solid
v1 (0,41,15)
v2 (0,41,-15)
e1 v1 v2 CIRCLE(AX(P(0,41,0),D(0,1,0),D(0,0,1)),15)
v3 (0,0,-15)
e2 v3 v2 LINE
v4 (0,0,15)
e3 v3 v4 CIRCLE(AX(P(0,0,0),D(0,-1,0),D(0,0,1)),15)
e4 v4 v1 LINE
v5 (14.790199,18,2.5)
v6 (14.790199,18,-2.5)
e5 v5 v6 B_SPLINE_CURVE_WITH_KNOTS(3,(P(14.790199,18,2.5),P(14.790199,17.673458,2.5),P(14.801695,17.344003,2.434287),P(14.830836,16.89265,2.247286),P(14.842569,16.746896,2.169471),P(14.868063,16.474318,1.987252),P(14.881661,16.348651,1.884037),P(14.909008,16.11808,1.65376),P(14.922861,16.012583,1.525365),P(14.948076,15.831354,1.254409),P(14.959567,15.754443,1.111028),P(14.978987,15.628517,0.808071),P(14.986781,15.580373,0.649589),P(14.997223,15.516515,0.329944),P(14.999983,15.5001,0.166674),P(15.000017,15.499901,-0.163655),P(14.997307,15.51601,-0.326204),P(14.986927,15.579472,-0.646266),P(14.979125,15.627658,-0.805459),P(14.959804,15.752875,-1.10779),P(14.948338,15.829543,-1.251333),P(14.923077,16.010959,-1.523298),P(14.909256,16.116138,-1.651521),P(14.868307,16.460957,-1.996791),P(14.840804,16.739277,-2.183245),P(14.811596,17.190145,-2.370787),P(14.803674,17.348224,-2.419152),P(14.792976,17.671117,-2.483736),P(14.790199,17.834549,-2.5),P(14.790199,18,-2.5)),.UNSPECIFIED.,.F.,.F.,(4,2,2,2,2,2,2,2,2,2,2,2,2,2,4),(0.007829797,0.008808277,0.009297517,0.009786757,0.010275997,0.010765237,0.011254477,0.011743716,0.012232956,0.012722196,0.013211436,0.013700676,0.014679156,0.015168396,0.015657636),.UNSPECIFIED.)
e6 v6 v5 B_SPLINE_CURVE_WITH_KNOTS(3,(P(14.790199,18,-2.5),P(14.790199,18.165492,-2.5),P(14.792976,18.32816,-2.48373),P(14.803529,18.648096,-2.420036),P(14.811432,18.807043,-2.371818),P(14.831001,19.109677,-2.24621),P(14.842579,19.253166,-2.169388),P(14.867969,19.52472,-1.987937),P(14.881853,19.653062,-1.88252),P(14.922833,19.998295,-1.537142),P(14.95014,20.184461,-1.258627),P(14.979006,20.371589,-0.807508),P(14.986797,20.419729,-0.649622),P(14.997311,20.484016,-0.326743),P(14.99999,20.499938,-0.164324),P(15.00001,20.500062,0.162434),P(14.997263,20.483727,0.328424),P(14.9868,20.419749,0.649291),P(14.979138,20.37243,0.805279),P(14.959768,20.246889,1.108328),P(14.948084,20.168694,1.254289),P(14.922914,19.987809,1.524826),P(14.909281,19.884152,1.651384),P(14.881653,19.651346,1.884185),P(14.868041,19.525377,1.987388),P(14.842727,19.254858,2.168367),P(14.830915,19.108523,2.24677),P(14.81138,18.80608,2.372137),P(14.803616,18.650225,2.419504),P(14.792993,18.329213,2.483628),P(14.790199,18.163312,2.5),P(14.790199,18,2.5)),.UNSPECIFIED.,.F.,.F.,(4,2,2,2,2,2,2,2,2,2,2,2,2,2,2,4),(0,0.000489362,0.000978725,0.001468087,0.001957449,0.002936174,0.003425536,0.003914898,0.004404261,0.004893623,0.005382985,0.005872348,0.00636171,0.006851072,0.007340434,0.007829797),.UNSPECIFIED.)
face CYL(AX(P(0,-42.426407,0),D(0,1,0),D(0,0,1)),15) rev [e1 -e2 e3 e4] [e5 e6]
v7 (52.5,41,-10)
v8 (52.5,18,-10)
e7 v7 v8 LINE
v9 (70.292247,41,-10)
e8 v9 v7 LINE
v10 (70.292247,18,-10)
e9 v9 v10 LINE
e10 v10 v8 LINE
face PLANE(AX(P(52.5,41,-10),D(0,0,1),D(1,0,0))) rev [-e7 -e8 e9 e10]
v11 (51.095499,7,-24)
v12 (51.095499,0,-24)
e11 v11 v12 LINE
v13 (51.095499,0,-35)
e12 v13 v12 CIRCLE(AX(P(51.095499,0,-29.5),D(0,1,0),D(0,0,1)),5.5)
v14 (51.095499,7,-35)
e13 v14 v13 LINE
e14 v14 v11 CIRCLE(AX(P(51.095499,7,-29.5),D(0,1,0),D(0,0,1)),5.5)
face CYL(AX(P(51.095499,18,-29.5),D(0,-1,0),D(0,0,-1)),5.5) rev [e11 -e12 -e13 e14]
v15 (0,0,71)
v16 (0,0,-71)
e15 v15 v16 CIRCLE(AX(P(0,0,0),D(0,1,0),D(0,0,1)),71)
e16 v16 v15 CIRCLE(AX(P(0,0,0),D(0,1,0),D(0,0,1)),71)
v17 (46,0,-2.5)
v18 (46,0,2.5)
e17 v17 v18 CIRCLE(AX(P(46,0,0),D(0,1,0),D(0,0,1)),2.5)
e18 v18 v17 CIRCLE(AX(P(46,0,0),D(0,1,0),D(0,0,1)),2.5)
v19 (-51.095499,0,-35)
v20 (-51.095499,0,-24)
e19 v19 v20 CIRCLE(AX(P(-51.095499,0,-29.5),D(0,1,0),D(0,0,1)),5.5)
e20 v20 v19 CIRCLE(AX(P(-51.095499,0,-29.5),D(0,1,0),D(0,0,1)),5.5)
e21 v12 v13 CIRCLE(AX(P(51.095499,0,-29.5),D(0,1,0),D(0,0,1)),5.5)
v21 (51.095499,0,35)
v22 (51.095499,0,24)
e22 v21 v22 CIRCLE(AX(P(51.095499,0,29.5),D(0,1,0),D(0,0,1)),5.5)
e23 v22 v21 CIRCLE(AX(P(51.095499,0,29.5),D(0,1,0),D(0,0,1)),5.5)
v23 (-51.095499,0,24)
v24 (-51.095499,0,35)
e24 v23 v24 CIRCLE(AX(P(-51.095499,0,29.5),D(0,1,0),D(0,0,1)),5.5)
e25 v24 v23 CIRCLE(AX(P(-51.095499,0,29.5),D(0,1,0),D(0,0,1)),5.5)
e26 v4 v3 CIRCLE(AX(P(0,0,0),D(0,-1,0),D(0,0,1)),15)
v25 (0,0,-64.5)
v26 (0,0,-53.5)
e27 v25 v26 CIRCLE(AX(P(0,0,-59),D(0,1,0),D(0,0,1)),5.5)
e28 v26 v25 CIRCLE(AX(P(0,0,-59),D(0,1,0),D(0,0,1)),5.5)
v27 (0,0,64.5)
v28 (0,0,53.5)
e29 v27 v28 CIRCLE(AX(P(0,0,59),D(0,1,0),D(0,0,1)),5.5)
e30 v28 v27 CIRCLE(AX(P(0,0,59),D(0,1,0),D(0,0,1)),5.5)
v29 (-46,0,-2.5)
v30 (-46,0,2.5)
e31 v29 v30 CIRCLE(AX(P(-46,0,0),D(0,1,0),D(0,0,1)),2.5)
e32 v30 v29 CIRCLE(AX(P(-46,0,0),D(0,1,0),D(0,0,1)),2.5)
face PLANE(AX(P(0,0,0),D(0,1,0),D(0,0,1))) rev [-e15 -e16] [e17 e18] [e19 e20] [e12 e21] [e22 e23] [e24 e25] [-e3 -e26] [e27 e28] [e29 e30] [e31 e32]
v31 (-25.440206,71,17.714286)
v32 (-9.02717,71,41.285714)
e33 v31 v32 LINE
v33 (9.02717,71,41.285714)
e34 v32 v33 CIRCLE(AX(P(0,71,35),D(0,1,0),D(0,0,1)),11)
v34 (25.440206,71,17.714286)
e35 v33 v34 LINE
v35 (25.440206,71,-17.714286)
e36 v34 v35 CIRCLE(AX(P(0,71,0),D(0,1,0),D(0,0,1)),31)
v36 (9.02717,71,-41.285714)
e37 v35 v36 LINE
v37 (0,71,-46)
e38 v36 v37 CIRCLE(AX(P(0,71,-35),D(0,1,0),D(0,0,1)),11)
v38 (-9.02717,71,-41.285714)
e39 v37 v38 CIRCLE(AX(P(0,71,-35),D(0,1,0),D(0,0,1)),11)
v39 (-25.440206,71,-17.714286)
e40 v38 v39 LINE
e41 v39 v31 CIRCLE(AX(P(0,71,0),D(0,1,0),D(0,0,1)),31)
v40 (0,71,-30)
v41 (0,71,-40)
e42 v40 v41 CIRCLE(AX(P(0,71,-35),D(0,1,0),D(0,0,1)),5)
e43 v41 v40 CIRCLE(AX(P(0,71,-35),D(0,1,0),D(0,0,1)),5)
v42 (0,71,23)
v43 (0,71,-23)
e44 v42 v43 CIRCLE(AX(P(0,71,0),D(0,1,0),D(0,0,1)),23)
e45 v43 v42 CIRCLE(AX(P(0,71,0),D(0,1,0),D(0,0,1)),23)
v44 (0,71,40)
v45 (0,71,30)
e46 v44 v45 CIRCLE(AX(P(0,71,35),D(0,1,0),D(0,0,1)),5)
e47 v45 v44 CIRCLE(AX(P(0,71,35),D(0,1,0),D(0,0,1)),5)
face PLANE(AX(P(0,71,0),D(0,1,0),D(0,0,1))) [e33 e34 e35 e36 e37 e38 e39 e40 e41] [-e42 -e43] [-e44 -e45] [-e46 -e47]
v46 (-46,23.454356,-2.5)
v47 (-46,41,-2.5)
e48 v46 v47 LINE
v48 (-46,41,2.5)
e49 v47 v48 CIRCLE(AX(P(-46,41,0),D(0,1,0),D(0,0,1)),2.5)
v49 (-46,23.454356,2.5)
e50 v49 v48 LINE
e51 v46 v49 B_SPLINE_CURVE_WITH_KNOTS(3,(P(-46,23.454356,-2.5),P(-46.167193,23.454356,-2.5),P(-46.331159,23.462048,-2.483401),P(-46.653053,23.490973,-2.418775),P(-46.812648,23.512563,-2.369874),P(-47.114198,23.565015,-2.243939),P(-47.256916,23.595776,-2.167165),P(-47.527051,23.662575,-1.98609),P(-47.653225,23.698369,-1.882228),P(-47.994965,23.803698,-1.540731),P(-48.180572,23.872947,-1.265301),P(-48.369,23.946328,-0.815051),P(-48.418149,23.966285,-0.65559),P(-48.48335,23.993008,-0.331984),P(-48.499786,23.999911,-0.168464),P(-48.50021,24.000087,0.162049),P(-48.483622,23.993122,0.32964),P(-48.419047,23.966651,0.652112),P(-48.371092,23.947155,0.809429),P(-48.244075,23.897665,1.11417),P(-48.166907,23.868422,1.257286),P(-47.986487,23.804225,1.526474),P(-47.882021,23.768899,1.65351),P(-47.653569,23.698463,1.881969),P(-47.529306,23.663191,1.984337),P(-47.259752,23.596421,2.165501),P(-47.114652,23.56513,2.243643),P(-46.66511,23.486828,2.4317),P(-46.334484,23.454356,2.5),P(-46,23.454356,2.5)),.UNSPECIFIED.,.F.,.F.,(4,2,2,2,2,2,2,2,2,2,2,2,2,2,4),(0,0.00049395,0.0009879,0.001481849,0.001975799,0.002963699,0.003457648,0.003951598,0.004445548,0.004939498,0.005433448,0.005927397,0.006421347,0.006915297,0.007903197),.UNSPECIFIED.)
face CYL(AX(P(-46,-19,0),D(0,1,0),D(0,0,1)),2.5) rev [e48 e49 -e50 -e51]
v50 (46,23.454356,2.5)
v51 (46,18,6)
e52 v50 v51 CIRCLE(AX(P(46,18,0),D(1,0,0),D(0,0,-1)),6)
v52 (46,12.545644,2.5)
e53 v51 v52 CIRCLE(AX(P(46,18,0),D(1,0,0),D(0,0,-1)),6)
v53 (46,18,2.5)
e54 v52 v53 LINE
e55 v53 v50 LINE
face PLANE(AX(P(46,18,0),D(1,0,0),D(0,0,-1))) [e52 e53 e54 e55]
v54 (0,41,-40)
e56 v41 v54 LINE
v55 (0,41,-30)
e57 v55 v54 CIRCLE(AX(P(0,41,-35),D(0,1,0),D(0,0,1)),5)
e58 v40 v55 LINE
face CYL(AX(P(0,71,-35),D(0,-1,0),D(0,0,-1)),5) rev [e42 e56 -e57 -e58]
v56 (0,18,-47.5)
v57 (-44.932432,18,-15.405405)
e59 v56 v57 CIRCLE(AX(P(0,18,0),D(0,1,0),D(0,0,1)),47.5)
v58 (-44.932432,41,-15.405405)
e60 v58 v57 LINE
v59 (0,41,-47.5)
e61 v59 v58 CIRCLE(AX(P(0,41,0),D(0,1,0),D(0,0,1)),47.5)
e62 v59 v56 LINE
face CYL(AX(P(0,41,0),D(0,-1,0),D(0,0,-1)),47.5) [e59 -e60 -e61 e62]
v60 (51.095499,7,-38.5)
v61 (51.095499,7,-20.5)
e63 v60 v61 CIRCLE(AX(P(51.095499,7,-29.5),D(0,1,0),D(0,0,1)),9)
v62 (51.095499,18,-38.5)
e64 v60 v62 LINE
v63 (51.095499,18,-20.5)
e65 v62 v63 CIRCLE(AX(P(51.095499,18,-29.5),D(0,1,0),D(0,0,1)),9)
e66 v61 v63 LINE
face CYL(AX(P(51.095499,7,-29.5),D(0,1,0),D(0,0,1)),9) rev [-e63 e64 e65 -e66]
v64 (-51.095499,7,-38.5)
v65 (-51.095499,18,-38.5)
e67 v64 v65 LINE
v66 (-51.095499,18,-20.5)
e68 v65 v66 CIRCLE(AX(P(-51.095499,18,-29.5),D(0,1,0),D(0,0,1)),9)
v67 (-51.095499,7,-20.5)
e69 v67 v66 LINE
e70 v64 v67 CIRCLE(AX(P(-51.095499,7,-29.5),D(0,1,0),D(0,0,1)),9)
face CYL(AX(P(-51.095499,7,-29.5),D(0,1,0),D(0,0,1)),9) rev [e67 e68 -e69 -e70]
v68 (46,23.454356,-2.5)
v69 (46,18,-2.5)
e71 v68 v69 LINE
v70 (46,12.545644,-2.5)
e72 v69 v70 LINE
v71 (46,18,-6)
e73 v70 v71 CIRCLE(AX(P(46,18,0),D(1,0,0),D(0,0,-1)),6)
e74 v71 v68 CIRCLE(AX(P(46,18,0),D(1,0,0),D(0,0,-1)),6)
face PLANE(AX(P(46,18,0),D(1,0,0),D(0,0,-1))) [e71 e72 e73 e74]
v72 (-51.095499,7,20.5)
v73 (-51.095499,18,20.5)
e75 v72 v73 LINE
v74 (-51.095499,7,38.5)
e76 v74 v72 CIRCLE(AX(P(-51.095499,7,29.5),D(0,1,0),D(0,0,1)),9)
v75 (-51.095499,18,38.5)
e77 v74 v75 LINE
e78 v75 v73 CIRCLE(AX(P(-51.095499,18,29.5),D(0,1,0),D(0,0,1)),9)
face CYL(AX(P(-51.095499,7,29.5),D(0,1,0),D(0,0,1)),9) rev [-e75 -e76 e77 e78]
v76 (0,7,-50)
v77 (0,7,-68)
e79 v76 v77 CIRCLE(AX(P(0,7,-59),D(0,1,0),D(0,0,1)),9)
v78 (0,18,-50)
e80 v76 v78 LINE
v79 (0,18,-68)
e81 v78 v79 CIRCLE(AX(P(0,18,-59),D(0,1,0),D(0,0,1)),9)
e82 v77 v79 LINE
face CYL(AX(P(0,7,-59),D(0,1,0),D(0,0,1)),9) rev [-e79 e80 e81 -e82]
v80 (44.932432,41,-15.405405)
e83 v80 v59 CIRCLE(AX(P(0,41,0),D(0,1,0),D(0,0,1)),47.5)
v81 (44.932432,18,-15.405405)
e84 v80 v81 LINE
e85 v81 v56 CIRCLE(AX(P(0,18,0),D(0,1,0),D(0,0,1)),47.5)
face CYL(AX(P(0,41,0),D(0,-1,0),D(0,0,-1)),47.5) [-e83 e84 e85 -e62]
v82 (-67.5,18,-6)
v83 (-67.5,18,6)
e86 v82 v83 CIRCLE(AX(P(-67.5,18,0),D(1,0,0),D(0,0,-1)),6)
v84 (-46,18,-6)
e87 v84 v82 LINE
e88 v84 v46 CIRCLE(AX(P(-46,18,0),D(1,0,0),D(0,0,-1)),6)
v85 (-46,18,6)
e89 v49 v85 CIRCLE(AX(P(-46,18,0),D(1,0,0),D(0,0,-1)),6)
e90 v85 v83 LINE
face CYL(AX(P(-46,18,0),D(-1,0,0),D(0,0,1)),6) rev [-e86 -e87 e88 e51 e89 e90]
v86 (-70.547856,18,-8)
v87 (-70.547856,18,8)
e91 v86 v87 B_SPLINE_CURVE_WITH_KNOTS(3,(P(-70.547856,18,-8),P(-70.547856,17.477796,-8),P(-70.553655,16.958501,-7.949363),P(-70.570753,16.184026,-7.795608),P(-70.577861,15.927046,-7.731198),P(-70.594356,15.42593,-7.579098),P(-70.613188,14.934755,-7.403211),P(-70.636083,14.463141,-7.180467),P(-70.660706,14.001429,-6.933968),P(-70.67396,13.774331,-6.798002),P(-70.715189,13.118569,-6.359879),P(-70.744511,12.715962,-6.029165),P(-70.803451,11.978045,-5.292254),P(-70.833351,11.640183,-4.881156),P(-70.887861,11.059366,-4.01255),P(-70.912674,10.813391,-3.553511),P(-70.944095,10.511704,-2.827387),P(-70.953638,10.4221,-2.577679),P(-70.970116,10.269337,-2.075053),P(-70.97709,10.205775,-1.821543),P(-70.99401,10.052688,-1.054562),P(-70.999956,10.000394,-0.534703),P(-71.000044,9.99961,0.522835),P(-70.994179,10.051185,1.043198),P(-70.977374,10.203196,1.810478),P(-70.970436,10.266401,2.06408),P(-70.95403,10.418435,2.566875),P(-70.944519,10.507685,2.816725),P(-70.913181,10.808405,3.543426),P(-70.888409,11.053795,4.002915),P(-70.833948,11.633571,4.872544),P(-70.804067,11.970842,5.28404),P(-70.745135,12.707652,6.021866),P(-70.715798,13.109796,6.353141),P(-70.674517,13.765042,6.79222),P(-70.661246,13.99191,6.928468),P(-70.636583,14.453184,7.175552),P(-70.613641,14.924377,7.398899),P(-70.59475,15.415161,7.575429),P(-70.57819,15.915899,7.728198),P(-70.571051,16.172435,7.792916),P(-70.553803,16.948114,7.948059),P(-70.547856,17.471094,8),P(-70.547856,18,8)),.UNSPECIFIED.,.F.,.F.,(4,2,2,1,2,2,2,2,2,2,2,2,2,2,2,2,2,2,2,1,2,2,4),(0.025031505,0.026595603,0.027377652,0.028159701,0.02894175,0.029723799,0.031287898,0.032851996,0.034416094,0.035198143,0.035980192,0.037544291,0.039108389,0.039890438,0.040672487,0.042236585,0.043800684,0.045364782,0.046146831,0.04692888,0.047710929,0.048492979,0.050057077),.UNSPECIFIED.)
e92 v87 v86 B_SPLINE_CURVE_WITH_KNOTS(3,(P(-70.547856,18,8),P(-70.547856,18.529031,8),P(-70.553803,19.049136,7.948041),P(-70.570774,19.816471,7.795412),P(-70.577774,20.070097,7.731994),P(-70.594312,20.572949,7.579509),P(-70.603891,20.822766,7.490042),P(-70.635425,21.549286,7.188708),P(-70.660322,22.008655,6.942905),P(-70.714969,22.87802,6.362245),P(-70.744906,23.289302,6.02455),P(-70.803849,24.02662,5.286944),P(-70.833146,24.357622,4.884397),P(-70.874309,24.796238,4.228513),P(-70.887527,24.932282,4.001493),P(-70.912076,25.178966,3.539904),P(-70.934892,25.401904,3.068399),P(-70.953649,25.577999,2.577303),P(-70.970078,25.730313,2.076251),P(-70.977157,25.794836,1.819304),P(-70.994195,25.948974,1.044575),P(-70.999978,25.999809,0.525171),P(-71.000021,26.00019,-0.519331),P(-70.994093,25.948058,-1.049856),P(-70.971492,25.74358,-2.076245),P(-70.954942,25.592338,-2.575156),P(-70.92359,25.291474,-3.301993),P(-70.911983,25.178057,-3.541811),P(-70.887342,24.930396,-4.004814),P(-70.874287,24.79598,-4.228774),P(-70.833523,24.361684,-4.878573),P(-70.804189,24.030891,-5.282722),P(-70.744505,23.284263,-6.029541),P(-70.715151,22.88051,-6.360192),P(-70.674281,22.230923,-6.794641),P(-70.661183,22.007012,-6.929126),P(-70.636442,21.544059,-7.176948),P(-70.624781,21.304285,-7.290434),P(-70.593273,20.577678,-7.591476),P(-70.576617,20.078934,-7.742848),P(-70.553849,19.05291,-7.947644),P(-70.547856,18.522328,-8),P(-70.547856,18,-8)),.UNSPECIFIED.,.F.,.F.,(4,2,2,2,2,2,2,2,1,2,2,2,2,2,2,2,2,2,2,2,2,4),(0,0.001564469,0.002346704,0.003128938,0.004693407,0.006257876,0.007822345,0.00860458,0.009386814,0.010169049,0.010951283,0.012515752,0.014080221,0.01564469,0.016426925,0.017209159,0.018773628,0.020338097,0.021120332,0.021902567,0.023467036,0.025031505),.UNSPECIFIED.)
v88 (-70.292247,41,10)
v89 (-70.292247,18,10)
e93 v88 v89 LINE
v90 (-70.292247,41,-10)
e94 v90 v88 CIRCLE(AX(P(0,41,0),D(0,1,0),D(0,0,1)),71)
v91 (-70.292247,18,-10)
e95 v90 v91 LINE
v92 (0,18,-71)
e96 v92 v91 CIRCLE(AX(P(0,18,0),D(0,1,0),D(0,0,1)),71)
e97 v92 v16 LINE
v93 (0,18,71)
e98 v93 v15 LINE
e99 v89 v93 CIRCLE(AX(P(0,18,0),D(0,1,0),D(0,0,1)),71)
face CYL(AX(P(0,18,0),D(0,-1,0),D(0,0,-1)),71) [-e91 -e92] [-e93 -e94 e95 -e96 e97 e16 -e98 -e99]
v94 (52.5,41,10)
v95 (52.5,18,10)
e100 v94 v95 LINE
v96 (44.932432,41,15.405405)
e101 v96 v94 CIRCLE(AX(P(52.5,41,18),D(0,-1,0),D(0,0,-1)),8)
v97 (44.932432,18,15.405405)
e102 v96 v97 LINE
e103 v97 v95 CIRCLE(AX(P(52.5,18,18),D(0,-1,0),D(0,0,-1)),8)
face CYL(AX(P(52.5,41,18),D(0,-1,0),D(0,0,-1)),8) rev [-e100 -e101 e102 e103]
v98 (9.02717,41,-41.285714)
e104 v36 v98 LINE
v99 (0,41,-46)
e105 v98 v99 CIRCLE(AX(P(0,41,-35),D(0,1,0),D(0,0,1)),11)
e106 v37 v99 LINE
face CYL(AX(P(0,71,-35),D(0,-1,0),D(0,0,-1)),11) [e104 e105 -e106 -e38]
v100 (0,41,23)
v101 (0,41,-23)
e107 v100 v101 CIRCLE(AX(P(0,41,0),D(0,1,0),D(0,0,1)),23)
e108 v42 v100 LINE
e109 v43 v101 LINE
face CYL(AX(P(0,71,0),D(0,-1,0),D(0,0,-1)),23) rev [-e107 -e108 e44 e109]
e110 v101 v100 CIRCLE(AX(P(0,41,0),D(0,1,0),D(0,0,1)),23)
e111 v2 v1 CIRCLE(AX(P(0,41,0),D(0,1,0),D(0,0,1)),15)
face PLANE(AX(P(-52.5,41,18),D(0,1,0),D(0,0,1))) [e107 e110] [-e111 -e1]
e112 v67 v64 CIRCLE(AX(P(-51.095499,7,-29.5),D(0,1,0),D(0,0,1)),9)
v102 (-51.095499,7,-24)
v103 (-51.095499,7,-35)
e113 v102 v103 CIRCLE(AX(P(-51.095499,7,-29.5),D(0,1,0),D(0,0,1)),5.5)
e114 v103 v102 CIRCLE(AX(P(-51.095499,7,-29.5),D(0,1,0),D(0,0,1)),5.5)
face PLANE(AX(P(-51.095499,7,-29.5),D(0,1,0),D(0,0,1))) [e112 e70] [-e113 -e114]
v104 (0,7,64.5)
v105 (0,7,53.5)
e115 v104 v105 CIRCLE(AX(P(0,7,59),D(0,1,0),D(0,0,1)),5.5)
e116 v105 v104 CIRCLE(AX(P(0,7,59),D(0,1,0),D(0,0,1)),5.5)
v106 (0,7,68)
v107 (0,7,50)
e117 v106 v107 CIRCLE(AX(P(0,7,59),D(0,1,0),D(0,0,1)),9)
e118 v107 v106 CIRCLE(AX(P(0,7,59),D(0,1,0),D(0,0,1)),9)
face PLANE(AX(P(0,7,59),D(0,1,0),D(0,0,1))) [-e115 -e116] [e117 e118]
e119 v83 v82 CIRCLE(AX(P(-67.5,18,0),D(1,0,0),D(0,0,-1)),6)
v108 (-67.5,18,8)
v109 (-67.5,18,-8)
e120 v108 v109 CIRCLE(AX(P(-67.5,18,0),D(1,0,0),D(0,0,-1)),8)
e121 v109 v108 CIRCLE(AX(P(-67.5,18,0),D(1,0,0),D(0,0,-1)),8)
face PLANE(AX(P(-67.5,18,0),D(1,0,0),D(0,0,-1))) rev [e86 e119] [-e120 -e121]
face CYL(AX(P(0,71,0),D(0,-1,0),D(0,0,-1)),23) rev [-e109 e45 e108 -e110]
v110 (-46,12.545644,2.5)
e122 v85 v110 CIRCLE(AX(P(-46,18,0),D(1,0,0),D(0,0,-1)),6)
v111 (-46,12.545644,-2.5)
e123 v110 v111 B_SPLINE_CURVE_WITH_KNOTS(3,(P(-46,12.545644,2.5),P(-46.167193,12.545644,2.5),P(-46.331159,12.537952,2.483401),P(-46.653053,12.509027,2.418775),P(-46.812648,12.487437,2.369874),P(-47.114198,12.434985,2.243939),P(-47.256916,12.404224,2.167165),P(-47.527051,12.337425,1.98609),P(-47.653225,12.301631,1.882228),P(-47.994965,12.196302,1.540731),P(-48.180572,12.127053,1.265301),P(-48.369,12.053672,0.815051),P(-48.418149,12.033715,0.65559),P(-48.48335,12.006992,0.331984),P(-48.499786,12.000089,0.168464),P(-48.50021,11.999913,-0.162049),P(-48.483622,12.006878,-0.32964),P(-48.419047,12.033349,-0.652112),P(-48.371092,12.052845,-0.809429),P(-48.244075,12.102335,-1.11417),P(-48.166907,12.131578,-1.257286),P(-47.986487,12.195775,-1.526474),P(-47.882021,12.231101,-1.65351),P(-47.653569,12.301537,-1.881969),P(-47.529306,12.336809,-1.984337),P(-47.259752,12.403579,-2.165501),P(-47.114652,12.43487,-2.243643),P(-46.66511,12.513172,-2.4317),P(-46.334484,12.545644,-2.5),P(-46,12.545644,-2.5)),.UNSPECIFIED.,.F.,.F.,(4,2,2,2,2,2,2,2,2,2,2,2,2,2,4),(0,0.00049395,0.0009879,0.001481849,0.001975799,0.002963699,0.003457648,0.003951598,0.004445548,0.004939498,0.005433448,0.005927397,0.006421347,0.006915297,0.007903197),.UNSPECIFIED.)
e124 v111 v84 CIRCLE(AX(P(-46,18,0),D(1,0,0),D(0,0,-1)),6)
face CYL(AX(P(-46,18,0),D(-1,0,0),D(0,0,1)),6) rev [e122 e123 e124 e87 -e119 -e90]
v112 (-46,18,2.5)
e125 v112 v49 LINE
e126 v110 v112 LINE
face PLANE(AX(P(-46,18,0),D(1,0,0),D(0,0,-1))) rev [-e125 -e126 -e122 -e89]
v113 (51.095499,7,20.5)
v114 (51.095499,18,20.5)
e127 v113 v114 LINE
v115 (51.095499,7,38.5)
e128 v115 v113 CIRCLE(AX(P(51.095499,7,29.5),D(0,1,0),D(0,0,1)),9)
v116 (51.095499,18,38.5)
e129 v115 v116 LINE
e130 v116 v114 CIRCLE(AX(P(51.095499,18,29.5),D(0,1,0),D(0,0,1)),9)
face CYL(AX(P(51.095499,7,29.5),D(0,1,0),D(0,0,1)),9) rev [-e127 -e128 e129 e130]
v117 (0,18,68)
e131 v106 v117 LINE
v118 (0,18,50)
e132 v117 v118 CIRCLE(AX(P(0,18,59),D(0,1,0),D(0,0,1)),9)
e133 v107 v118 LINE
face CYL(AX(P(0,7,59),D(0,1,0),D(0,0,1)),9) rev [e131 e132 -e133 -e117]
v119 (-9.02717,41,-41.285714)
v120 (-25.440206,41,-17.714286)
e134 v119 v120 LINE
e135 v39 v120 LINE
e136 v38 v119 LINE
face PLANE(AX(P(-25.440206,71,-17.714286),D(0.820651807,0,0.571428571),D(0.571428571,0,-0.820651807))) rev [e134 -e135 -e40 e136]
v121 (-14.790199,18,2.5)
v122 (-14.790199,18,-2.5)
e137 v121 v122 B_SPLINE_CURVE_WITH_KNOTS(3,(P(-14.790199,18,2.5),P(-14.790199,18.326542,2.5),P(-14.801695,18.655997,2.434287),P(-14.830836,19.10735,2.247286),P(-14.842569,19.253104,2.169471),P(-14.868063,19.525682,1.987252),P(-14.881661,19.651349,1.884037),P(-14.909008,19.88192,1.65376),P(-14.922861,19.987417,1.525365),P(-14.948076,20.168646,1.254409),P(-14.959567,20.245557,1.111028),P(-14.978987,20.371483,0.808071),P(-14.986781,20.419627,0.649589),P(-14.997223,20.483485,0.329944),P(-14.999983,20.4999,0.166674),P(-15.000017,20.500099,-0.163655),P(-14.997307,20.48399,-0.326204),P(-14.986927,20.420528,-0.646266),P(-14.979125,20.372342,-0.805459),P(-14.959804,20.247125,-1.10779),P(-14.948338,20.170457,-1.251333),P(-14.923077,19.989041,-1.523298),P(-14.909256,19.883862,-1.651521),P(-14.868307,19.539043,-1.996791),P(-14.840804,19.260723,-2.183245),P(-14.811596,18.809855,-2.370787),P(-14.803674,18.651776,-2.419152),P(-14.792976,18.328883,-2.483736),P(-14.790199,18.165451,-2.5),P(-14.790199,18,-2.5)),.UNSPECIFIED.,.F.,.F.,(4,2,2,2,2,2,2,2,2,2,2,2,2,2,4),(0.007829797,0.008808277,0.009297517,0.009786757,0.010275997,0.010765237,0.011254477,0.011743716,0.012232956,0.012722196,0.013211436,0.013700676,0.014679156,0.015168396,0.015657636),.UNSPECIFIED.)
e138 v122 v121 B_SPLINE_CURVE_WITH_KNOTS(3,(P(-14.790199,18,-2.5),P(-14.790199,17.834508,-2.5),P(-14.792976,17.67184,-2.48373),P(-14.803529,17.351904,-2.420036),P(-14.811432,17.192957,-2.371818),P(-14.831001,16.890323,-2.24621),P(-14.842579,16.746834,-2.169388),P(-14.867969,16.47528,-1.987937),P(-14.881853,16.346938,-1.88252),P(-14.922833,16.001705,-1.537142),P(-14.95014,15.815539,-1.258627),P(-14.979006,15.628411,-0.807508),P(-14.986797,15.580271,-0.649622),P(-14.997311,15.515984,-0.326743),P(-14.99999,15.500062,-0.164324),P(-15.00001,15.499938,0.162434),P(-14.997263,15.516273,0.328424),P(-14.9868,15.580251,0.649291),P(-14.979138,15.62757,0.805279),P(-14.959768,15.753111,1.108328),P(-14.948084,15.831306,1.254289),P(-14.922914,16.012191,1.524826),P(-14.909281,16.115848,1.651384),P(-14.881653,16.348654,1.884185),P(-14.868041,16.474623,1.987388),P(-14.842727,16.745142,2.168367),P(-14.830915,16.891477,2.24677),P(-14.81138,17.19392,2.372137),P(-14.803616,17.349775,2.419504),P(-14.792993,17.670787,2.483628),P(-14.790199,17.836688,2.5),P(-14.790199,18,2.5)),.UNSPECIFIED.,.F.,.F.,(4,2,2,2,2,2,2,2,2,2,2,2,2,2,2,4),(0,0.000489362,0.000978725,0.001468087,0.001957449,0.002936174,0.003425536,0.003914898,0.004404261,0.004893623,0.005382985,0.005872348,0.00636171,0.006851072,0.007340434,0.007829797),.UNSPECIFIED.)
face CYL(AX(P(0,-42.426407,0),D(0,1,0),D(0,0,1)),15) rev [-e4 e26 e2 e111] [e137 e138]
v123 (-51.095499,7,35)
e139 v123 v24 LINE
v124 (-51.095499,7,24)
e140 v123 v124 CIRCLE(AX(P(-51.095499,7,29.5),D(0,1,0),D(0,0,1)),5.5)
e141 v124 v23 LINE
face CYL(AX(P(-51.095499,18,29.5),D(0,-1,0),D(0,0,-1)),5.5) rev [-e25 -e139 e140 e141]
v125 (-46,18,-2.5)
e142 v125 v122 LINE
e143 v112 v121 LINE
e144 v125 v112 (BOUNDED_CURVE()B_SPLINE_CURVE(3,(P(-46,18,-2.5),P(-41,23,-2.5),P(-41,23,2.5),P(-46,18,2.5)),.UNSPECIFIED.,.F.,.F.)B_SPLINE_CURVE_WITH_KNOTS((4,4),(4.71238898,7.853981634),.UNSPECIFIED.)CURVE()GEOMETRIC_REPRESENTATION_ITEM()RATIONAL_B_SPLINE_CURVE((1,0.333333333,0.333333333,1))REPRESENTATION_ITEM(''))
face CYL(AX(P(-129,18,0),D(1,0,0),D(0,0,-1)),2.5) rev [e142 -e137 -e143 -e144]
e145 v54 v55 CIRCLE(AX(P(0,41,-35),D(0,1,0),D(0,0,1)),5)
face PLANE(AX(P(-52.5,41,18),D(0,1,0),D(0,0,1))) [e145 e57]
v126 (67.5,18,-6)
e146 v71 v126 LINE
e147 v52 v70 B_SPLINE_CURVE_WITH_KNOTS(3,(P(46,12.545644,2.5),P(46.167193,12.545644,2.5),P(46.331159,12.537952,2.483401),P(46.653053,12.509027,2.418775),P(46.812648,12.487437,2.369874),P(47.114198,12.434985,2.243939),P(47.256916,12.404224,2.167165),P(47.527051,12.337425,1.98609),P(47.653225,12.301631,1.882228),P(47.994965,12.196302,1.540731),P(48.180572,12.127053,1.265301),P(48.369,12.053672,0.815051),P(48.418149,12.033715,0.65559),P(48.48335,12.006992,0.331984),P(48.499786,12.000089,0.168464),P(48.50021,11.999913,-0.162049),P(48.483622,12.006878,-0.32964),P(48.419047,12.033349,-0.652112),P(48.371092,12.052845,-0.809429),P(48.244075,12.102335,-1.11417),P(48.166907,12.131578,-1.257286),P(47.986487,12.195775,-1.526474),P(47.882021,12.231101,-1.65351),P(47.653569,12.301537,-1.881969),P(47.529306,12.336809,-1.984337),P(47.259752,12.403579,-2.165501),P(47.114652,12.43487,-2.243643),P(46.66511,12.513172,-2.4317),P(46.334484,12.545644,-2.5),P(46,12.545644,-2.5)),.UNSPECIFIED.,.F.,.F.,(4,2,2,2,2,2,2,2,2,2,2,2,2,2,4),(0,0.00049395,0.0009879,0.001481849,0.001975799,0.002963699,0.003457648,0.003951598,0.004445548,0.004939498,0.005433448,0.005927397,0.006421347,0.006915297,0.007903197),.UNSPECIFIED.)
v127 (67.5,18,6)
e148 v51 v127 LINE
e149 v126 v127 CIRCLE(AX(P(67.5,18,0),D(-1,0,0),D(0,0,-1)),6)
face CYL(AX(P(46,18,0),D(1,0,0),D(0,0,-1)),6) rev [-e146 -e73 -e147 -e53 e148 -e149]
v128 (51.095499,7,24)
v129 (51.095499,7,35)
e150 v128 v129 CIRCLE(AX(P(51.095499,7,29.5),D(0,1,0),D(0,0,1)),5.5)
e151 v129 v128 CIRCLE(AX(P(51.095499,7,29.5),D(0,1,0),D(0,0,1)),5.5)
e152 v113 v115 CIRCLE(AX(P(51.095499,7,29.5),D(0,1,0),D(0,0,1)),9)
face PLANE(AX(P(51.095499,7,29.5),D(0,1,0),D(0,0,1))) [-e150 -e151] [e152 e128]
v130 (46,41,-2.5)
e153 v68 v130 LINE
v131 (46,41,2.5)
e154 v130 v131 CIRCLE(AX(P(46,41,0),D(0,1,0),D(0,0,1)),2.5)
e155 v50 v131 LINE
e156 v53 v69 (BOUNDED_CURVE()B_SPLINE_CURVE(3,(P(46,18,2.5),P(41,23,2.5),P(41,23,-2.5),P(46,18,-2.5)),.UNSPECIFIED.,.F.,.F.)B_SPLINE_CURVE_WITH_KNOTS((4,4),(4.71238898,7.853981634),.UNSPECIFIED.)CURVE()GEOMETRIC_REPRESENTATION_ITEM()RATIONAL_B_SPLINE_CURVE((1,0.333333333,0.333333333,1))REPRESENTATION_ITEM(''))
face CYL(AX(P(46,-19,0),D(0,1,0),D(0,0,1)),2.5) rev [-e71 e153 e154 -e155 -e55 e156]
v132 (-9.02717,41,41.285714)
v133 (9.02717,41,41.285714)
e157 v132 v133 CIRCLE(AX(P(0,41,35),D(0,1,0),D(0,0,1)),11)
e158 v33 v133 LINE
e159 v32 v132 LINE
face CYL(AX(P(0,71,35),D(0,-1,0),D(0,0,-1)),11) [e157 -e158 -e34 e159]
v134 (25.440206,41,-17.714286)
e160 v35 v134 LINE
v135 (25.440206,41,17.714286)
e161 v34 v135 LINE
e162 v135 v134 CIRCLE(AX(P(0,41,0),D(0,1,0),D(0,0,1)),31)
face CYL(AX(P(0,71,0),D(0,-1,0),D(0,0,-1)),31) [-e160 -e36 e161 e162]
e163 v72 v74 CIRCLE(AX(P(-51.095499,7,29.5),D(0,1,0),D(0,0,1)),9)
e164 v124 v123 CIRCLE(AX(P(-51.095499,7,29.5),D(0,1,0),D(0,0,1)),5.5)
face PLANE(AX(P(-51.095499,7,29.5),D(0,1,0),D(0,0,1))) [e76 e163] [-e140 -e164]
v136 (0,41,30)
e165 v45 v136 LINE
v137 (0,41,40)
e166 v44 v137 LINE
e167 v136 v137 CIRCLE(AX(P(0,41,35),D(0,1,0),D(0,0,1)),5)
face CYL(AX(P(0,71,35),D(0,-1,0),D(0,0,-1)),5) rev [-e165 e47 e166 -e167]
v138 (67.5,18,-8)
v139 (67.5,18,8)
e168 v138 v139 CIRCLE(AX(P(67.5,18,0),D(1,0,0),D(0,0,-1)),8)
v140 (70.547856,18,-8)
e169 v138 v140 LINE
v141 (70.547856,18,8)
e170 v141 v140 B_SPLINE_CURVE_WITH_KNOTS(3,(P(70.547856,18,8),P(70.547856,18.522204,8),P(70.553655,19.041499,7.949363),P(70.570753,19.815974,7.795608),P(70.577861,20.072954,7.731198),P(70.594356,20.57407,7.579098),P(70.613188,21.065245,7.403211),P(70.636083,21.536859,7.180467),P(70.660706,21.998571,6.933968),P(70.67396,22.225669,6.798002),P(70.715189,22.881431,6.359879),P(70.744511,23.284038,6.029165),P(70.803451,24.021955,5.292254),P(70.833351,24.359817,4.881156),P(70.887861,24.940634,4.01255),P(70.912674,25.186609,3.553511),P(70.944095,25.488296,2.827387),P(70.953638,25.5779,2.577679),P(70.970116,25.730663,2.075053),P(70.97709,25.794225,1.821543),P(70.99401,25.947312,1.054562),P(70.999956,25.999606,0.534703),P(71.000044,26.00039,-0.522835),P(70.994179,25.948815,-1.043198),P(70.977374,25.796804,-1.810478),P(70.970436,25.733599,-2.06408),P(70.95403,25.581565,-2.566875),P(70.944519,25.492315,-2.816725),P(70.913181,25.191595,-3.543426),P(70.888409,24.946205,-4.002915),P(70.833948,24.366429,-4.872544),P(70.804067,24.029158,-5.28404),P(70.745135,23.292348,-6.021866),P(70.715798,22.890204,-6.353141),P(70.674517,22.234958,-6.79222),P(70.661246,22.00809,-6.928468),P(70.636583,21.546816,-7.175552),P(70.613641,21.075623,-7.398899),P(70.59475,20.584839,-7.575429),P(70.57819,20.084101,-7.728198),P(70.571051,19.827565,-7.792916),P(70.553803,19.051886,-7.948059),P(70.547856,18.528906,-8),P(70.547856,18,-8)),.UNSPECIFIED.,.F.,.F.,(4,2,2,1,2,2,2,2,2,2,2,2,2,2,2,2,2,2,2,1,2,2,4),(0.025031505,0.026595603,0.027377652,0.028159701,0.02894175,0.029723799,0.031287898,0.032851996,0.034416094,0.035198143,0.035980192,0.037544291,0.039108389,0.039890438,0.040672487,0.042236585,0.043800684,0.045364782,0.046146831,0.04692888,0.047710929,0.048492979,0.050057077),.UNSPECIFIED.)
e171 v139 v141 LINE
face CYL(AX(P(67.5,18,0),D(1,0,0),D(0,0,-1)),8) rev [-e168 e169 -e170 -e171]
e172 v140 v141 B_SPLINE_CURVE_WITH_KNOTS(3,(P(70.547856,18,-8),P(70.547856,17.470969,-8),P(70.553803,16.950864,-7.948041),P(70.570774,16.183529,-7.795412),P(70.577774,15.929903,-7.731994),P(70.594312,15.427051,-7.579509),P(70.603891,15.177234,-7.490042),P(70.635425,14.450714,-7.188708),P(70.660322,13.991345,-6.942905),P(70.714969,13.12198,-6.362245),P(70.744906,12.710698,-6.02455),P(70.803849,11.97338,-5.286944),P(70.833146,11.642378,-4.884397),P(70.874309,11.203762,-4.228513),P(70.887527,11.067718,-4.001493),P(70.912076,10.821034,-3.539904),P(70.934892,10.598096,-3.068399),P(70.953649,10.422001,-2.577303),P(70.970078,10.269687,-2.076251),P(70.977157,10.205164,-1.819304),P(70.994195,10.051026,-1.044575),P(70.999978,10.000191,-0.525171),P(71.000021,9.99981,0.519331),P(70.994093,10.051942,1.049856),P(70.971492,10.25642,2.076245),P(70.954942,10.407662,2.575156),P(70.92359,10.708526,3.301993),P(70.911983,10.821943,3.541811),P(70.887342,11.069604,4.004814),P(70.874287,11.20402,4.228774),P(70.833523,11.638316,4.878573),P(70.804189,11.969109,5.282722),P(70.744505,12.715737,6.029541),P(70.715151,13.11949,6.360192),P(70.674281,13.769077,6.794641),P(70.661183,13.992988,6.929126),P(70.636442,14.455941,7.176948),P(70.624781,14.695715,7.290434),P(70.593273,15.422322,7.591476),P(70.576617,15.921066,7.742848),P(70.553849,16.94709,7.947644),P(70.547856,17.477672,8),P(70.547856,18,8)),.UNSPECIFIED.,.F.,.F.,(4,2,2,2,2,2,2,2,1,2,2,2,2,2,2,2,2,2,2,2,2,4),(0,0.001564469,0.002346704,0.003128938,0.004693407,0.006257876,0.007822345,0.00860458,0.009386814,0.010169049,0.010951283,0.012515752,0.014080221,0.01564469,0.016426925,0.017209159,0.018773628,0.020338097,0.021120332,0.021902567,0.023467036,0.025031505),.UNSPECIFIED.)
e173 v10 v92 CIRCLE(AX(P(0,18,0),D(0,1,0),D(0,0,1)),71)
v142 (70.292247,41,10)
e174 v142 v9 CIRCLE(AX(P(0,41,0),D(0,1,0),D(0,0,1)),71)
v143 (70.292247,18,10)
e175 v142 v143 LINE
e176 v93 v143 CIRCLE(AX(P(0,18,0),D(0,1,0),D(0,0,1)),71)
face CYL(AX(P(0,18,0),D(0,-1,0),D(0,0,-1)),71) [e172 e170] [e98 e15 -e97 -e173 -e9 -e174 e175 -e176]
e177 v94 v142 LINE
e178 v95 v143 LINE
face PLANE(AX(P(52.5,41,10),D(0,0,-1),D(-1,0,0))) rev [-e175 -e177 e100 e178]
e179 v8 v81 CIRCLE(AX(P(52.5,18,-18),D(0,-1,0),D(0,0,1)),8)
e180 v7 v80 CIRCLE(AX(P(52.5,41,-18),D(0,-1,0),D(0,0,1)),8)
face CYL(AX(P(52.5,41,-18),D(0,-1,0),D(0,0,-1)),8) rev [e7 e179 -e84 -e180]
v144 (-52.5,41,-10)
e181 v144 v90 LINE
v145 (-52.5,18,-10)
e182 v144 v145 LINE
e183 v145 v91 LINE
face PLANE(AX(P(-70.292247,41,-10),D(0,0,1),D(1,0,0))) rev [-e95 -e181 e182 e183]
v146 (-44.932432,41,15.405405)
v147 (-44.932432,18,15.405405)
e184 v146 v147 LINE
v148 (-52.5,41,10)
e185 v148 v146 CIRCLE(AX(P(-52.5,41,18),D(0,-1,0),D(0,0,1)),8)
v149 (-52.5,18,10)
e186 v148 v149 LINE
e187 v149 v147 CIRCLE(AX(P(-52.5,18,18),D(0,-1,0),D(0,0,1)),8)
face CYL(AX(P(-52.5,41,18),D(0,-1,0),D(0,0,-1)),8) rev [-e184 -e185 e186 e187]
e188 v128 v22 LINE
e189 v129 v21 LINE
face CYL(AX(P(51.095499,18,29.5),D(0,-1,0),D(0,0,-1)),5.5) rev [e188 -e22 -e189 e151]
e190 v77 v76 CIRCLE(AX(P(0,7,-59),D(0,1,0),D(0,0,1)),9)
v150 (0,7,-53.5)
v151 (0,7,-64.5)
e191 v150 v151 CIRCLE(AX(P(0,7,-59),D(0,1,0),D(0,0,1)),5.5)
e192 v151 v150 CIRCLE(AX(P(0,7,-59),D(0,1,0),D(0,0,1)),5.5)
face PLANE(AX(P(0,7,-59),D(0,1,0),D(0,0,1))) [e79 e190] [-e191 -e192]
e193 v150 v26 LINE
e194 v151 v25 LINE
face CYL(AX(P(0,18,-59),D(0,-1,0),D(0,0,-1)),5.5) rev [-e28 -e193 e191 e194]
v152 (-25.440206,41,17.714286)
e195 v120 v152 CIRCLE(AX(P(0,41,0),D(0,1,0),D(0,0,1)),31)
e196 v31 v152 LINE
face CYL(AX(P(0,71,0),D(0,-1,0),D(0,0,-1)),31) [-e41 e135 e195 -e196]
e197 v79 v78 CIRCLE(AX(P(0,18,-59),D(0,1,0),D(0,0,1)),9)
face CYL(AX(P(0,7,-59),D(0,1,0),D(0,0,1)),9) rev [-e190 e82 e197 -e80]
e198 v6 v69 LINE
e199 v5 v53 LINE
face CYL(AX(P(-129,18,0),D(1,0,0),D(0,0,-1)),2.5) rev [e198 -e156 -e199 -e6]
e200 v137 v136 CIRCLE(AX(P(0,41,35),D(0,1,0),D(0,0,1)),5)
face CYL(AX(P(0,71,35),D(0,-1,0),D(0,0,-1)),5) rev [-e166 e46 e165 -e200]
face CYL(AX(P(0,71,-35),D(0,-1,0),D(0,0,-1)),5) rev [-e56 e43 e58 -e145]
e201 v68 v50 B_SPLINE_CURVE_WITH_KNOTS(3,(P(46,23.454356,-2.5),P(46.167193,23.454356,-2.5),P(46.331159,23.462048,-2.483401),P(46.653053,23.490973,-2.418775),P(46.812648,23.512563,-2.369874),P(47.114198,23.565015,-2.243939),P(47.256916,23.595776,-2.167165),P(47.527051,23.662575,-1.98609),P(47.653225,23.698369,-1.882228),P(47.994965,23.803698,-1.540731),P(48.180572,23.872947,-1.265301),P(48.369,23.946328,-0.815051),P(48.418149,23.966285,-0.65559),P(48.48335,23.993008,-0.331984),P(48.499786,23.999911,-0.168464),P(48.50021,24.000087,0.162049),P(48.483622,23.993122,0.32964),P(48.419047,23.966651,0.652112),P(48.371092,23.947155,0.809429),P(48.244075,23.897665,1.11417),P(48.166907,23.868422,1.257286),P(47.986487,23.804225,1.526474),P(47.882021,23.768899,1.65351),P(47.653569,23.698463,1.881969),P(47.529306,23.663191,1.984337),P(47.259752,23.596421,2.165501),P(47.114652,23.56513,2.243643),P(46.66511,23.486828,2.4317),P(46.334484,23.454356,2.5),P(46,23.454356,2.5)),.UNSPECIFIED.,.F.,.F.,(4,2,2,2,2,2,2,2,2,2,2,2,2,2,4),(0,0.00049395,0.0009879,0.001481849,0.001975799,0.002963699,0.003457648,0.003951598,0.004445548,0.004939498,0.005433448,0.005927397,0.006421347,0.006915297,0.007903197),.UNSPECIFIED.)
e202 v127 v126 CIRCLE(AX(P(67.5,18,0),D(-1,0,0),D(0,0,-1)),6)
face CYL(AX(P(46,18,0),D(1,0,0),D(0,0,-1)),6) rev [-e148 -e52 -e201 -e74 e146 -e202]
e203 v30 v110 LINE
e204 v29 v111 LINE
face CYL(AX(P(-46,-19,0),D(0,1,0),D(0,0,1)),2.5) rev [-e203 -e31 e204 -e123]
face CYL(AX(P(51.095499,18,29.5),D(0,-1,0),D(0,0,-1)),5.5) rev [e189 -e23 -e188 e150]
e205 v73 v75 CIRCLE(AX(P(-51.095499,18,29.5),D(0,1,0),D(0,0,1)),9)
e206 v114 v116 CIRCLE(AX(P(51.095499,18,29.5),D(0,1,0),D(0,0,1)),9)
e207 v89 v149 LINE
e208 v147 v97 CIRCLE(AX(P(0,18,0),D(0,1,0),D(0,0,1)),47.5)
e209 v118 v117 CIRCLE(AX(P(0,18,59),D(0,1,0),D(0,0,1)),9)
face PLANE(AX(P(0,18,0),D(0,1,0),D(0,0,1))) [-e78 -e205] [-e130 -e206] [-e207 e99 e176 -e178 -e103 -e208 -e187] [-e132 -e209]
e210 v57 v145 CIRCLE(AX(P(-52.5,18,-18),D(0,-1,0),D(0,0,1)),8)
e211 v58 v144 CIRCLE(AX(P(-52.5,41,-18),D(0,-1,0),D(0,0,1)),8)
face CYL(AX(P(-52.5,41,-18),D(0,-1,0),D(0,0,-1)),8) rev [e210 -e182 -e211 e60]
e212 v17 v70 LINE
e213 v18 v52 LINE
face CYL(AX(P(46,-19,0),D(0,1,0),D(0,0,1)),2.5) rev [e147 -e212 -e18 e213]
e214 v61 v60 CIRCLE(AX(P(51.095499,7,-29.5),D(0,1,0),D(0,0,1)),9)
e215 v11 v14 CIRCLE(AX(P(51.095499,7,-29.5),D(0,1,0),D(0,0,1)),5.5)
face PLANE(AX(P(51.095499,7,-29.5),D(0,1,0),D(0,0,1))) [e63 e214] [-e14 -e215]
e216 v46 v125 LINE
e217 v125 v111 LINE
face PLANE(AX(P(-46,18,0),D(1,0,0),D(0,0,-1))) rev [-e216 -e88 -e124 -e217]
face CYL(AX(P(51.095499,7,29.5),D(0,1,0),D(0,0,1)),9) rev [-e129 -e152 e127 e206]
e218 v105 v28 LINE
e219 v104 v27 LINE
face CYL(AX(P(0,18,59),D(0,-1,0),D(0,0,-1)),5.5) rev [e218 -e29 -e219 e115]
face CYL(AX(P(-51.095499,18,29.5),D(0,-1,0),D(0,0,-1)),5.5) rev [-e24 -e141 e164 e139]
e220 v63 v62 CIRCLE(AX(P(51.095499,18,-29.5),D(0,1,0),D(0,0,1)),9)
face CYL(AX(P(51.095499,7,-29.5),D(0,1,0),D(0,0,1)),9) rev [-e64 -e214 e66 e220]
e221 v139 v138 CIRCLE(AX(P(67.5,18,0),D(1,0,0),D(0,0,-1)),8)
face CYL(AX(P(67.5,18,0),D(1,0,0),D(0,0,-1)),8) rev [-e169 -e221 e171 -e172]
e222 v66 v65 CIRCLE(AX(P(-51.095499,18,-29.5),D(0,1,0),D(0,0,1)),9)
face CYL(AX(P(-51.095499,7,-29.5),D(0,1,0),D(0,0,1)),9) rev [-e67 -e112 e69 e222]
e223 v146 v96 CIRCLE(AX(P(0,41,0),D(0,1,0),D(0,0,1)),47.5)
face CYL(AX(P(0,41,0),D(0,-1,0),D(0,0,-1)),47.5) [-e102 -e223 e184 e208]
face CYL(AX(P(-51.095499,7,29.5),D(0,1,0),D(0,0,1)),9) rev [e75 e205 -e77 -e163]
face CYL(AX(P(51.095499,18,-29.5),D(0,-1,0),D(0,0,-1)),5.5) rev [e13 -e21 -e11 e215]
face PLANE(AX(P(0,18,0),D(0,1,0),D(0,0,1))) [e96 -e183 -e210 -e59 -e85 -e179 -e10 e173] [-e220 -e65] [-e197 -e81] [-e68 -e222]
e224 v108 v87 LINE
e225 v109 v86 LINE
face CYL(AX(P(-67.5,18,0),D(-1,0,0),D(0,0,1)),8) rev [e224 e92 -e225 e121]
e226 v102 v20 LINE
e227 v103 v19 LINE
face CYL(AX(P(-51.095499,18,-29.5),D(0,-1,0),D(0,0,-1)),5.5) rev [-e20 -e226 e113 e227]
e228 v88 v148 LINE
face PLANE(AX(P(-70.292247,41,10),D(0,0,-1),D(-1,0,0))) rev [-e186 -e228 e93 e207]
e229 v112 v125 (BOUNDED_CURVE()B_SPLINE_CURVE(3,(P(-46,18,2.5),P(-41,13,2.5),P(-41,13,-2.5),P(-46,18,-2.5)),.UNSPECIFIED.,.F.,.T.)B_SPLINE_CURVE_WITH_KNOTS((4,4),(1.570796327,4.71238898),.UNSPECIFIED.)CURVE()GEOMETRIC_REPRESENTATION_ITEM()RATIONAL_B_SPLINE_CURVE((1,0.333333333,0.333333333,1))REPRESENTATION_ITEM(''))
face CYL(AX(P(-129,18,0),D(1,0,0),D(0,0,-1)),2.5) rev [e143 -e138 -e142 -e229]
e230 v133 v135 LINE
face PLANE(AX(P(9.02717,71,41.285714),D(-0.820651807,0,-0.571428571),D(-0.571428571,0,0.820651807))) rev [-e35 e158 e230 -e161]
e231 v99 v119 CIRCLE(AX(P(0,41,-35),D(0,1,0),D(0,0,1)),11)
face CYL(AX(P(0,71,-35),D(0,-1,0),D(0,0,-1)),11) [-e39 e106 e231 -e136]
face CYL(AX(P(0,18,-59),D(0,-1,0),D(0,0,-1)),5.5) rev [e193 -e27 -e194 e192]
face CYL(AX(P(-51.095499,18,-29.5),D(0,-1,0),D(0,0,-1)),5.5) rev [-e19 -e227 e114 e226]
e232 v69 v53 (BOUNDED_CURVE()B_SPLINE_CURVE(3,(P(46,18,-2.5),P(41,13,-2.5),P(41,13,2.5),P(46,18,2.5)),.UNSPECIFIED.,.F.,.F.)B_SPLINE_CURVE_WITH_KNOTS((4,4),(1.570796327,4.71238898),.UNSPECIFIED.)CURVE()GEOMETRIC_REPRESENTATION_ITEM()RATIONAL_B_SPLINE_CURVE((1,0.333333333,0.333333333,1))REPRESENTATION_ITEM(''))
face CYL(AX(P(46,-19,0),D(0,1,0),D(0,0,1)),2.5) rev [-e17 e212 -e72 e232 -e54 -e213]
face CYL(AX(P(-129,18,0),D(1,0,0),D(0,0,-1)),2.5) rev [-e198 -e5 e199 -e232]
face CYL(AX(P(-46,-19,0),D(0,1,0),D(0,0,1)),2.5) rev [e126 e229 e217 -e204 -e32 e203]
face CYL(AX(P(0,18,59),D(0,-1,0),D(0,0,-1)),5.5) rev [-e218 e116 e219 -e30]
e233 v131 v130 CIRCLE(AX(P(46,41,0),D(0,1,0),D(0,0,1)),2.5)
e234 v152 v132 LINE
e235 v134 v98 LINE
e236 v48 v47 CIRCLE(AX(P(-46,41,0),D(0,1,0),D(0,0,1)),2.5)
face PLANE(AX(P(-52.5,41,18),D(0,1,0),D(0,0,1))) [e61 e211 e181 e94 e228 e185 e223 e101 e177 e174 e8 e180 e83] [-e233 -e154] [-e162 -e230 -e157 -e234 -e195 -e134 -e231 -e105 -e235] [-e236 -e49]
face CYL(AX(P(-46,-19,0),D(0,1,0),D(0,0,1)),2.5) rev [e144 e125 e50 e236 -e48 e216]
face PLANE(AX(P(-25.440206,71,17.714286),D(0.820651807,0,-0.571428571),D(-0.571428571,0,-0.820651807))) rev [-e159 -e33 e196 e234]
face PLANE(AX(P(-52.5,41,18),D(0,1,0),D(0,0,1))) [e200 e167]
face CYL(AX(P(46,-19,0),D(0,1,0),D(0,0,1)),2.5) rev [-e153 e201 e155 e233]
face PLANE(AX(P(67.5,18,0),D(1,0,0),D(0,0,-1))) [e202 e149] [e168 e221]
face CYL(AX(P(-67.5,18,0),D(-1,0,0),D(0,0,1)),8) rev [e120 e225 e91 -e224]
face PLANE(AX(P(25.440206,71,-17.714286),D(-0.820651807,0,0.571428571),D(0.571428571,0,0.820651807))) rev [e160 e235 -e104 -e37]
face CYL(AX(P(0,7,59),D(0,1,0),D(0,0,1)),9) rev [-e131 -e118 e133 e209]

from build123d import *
from build123d.topology import SkipClean

# Parameters (mm, degrees)
BASE_FLANGE_SKETCH_R            = 71
BASE_FLANGE_SKETCH_R_2          = 5.5
BASE_FLANGE_142_6X_11_DEPTH     = 18
FLANGE_COUNTERBORE_SKETCH_R     = 9
FLANGE_COUNTERBORES_6X_18_DEPTH = 11
HUB_95_WITH_SIDE_LUGS_DEPTH     = 23
LOBED_CAP_SKETCH_R              = 5
LOBED_CAP_SKETCH_R_2            = 23
LOBED_CAP_BOSS_DEPTH            = 30
CAP_HOLES_SKETCH_R              = 2.5
CAP_HOLES_2X_5_DEPTH            = 60
BORE_SKETCH_R                   = 15
BORE_30_DEPTH                   = 71
CROSS_HOLE_SKETCH_R             = 2.5
CROSS_HOLE_5_DEPTH              = 200
SIDE_A_COUNTERBORE_SKETCH_R     = 6
SIDE_A_COUNTERBORE_12_DEPTH     = 25
SIDE_A_SPOTFACE_SKETCH_R        = 8
SIDE_A_SPOTFACE_16_DEPTH        = 3.5
SIDE_START                      = 25
SIDE_B_COUNTERBORE_SKETCH_R     = 6
SIDE_B_COUNTERBORE_12_DEPTH     = 25
SIDE_START_2                    = 3.5
SIDE_B_SPOTFACE_SKETCH_R        = 8
SIDE_B_SPOTFACE_16_DEPTH        = 3.5


with BuildPart() as part:
    # Base Flange Sketch → Base Flange Ø142 6xØ11 (new body)
    with BuildSketch(Plane(origin=(0, 0, 0), x_dir=(1, 0, 0), z_dir=(0, 1, 0))):
        with Locations(Location((0, 0, 0), (0, 0, 270))):
            Circle(BASE_FLANGE_SKETCH_R)
        with Locations(Location((0, 59, 0), (0, 0, 270))):
            Circle(BASE_FLANGE_SKETCH_R_2, mode=Mode.SUBTRACT)
        with Locations(Location((51.095498823, 29.5, 0), (0, 0, 270))):
            Circle(BASE_FLANGE_SKETCH_R_2, mode=Mode.SUBTRACT)
        with Locations(Location((51.095498823, -29.5, 0), (0, 0, 270))):
            Circle(BASE_FLANGE_SKETCH_R_2, mode=Mode.SUBTRACT)
        with Locations(Location((0, -59, 0), (0, 0, 270))):
            Circle(BASE_FLANGE_SKETCH_R_2, mode=Mode.SUBTRACT)
        with Locations(Location((-51.095498823, -29.5, 0), (0, 0, 270))):
            Circle(BASE_FLANGE_SKETCH_R_2, mode=Mode.SUBTRACT)
        with Locations(Location((-51.095498823, 29.5, 0), (0, 0, 270))):
            Circle(BASE_FLANGE_SKETCH_R_2, mode=Mode.SUBTRACT)
    extrude(amount=BASE_FLANGE_142_6X_11_DEPTH)

    # Flange Counterbore Sketch → Flange Counterbores 6xØ18 (cut)
    with BuildSketch(Plane(origin=(0, 18, 0), x_dir=(1, 0, 0), z_dir=(0, 1, 0))):
        with Locations(Location((0, 59, 0), (0, 0, 270))):
            Circle(FLANGE_COUNTERBORE_SKETCH_R)
        with Locations(Location((51.095498823, 29.5, 0), (0, 0, 270))):
            Circle(FLANGE_COUNTERBORE_SKETCH_R)
        with Locations(Location((51.095498823, -29.5, 0), (0, 0, 270))):
            Circle(FLANGE_COUNTERBORE_SKETCH_R)
        with Locations(Location((0, -59, 0), (0, 0, 270))):
            Circle(FLANGE_COUNTERBORE_SKETCH_R)
        with Locations(Location((-51.095498823, -29.5, 0), (0, 0, 270))):
            Circle(FLANGE_COUNTERBORE_SKETCH_R)
        with Locations(Location((-51.095498823, 29.5, 0), (0, 0, 270))):
            Circle(FLANGE_COUNTERBORE_SKETCH_R)
    extrude(amount=-FLANGE_COUNTERBORES_6X_18_DEPTH, mode=Mode.SUBTRACT)

    # Hub Sketch → Hub Ø95 with Side Lugs (add)
    with SkipClean():  # the faces are left unmerged after this step: merging them gives an invalid solid
        with BuildSketch(Plane(origin=(0, 18, 0), x_dir=(1, 0, 0), z_dir=(0, 1, 0))):
            with BuildLine():
                Line((52.5, 10), (70.292247083, 10))
                ThreePointArc((70.292247083, 10), (71, 0), (70.292247083, -10))
                Line((70.292247083, -10), (52.5, -10))
                ThreePointArc((52.5, -10), (47.85009445, -11.49013223), (44.932432432, -15.405405405))
                ThreePointArc((44.932432432, -15.405405405), (0, -47.5), (-44.932432432, -15.405405405))
                ThreePointArc((-44.932432432, -15.405405405), (-47.85009445, -11.49013223), (-52.5, -10))
                Line((-52.5, -10), (-70.292247083, -10))
                ThreePointArc((-70.292247083, -10), (-71, 0), (-70.292247083, 10))
                Line((-70.292247083, 10), (-52.5, 10))
                ThreePointArc((-52.5, 10), (-47.85009445, 11.49013223), (-44.932432432, 15.405405405))
                ThreePointArc((-44.932432432, 15.405405405), (0, 47.5), (44.932432432, 15.405405405))
                ThreePointArc((44.932432432, 15.405405405), (47.85009445, 11.49013223), (52.5, 10))
            make_face()
        extrude(amount=HUB_95_WITH_SIDE_LUGS_DEPTH)

    # Lobed Cap Sketch → Lobed Cap Boss (add)
    with SkipClean():  # the faces are left unmerged after this step: merging them gives an invalid solid
        with BuildSketch(Plane(origin=(0, 41, 0), x_dir=(1, 0, 0), z_dir=(0, 1, 0))):
            with BuildLine():
                Line((-25.440206006, 17.714285714), (-9.027169873, 41.285714286))
                ThreePointArc((-9.027169873, 41.285714286), (0, 46), (9.027169873, 41.285714286))
                Line((9.027169873, 41.285714286), (25.440206006, 17.714285714))
                ThreePointArc((25.440206006, 17.714285714), (31, 0), (25.440206006, -17.714285714))
                Line((25.440206006, -17.714285714), (9.027169873, -41.285714286))
                ThreePointArc((9.027169873, -41.285714286), (0, -46), (-9.027169873, -41.285714286))
                Line((-9.027169873, -41.285714286), (-25.440206006, -17.714285714))
                ThreePointArc((-25.440206006, -17.714285714), (-31, 0), (-25.440206006, 17.714285714))
            make_face()
            with Locations(Location((0, 35, 0), (0, 0, 270))):
                Circle(LOBED_CAP_SKETCH_R, mode=Mode.SUBTRACT)
            with Locations(Location((0, -35, 0), (0, 0, 270))):
                Circle(LOBED_CAP_SKETCH_R, mode=Mode.SUBTRACT)
            with Locations(Location((0, 0, 0), (0, 0, 270))):
                Circle(LOBED_CAP_SKETCH_R_2, mode=Mode.SUBTRACT)
        extrude(amount=LOBED_CAP_BOSS_DEPTH)

    # Cap Holes Sketch → Cap Holes 2xØ5 (cut)
    with SkipClean():  # the faces are left unmerged after this step: merging them gives an invalid solid
        with BuildSketch(Plane(origin=(0, 41, 0), x_dir=(1, 0, 0), z_dir=(0, 1, 0))):
            with Locations(Location((-46, 0, 0), (0, 0, 270))):
                Circle(CAP_HOLES_SKETCH_R)
            with Locations(Location((46, 0, 0), (0, 0, 270))):
                Circle(CAP_HOLES_SKETCH_R)
        extrude(amount=-CAP_HOLES_2X_5_DEPTH, mode=Mode.SUBTRACT)

    # Bore Sketch → Bore Ø30 (cut)
    with SkipClean():  # the faces are left unmerged after this step: merging them gives an invalid solid
        with BuildSketch(Plane(origin=(0, 71, 0), x_dir=(1, 0, 0), z_dir=(0, 1, 0))):
            with Locations(Location((0, 0, 0), (0, 0, 270))):
                Circle(BORE_SKETCH_R)
        extrude(amount=-BORE_30_DEPTH, mode=Mode.SUBTRACT)

    # Cross Hole Sketch → Cross Hole Ø5 (cut)
    with BuildSketch(Plane(origin=(71, 0, 0), x_dir=(0, 0, -1), z_dir=(1, 0, 0))):
        with Locations((0, 18)):
            Circle(CROSS_HOLE_SKETCH_R)
    extrude(amount=-CROSS_HOLE_5_DEPTH, mode=Mode.SUBTRACT)

    # Side A Counterbore Sketch → Side A Counterbore Ø12 (cut)
    with BuildSketch(Plane(origin=(71, 0, 0), x_dir=(0, 0, -1), z_dir=(1, 0, 0))):
        with Locations((0, 18)):
            Circle(SIDE_A_COUNTERBORE_SKETCH_R)
    extrude(amount=-SIDE_A_COUNTERBORE_12_DEPTH, mode=Mode.SUBTRACT)

    # Side A Spotface Sketch → Side A Spotface Ø16 (cut)
    with BuildSketch(Plane(origin=(71, 0, 0), x_dir=(0, 0, -1), z_dir=(1, 0, 0))):
        with Locations((0, 18)):
            Circle(SIDE_A_SPOTFACE_SKETCH_R)
    extrude(amount=-SIDE_A_SPOTFACE_16_DEPTH, mode=Mode.SUBTRACT)

    # Side B Counterbore Sketch → Side B Counterbore Ø12 (cut)
    with BuildSketch(Plane(origin=(-71, 0, 0), x_dir=(0, 0, -1), z_dir=(1, 0, 0)).offset(SIDE_START)):
        with Locations((0, 18)):
            Circle(SIDE_B_COUNTERBORE_SKETCH_R)
    extrude(amount=-SIDE_B_COUNTERBORE_12_DEPTH, mode=Mode.SUBTRACT)

    # Side B Spotface Sketch → Side B Spotface Ø16 (cut)
    with BuildSketch(Plane(origin=(-71, 0, 0), x_dir=(0, 0, -1), z_dir=(1, 0, 0)).offset(SIDE_START_2)):
        with Locations((0, 18)):
            Circle(SIDE_B_SPOTFACE_SKETCH_R)
    extrude(amount=-SIDE_B_SPOTFACE_16_DEPTH, mode=Mode.SUBTRACT)


solid = part.part
